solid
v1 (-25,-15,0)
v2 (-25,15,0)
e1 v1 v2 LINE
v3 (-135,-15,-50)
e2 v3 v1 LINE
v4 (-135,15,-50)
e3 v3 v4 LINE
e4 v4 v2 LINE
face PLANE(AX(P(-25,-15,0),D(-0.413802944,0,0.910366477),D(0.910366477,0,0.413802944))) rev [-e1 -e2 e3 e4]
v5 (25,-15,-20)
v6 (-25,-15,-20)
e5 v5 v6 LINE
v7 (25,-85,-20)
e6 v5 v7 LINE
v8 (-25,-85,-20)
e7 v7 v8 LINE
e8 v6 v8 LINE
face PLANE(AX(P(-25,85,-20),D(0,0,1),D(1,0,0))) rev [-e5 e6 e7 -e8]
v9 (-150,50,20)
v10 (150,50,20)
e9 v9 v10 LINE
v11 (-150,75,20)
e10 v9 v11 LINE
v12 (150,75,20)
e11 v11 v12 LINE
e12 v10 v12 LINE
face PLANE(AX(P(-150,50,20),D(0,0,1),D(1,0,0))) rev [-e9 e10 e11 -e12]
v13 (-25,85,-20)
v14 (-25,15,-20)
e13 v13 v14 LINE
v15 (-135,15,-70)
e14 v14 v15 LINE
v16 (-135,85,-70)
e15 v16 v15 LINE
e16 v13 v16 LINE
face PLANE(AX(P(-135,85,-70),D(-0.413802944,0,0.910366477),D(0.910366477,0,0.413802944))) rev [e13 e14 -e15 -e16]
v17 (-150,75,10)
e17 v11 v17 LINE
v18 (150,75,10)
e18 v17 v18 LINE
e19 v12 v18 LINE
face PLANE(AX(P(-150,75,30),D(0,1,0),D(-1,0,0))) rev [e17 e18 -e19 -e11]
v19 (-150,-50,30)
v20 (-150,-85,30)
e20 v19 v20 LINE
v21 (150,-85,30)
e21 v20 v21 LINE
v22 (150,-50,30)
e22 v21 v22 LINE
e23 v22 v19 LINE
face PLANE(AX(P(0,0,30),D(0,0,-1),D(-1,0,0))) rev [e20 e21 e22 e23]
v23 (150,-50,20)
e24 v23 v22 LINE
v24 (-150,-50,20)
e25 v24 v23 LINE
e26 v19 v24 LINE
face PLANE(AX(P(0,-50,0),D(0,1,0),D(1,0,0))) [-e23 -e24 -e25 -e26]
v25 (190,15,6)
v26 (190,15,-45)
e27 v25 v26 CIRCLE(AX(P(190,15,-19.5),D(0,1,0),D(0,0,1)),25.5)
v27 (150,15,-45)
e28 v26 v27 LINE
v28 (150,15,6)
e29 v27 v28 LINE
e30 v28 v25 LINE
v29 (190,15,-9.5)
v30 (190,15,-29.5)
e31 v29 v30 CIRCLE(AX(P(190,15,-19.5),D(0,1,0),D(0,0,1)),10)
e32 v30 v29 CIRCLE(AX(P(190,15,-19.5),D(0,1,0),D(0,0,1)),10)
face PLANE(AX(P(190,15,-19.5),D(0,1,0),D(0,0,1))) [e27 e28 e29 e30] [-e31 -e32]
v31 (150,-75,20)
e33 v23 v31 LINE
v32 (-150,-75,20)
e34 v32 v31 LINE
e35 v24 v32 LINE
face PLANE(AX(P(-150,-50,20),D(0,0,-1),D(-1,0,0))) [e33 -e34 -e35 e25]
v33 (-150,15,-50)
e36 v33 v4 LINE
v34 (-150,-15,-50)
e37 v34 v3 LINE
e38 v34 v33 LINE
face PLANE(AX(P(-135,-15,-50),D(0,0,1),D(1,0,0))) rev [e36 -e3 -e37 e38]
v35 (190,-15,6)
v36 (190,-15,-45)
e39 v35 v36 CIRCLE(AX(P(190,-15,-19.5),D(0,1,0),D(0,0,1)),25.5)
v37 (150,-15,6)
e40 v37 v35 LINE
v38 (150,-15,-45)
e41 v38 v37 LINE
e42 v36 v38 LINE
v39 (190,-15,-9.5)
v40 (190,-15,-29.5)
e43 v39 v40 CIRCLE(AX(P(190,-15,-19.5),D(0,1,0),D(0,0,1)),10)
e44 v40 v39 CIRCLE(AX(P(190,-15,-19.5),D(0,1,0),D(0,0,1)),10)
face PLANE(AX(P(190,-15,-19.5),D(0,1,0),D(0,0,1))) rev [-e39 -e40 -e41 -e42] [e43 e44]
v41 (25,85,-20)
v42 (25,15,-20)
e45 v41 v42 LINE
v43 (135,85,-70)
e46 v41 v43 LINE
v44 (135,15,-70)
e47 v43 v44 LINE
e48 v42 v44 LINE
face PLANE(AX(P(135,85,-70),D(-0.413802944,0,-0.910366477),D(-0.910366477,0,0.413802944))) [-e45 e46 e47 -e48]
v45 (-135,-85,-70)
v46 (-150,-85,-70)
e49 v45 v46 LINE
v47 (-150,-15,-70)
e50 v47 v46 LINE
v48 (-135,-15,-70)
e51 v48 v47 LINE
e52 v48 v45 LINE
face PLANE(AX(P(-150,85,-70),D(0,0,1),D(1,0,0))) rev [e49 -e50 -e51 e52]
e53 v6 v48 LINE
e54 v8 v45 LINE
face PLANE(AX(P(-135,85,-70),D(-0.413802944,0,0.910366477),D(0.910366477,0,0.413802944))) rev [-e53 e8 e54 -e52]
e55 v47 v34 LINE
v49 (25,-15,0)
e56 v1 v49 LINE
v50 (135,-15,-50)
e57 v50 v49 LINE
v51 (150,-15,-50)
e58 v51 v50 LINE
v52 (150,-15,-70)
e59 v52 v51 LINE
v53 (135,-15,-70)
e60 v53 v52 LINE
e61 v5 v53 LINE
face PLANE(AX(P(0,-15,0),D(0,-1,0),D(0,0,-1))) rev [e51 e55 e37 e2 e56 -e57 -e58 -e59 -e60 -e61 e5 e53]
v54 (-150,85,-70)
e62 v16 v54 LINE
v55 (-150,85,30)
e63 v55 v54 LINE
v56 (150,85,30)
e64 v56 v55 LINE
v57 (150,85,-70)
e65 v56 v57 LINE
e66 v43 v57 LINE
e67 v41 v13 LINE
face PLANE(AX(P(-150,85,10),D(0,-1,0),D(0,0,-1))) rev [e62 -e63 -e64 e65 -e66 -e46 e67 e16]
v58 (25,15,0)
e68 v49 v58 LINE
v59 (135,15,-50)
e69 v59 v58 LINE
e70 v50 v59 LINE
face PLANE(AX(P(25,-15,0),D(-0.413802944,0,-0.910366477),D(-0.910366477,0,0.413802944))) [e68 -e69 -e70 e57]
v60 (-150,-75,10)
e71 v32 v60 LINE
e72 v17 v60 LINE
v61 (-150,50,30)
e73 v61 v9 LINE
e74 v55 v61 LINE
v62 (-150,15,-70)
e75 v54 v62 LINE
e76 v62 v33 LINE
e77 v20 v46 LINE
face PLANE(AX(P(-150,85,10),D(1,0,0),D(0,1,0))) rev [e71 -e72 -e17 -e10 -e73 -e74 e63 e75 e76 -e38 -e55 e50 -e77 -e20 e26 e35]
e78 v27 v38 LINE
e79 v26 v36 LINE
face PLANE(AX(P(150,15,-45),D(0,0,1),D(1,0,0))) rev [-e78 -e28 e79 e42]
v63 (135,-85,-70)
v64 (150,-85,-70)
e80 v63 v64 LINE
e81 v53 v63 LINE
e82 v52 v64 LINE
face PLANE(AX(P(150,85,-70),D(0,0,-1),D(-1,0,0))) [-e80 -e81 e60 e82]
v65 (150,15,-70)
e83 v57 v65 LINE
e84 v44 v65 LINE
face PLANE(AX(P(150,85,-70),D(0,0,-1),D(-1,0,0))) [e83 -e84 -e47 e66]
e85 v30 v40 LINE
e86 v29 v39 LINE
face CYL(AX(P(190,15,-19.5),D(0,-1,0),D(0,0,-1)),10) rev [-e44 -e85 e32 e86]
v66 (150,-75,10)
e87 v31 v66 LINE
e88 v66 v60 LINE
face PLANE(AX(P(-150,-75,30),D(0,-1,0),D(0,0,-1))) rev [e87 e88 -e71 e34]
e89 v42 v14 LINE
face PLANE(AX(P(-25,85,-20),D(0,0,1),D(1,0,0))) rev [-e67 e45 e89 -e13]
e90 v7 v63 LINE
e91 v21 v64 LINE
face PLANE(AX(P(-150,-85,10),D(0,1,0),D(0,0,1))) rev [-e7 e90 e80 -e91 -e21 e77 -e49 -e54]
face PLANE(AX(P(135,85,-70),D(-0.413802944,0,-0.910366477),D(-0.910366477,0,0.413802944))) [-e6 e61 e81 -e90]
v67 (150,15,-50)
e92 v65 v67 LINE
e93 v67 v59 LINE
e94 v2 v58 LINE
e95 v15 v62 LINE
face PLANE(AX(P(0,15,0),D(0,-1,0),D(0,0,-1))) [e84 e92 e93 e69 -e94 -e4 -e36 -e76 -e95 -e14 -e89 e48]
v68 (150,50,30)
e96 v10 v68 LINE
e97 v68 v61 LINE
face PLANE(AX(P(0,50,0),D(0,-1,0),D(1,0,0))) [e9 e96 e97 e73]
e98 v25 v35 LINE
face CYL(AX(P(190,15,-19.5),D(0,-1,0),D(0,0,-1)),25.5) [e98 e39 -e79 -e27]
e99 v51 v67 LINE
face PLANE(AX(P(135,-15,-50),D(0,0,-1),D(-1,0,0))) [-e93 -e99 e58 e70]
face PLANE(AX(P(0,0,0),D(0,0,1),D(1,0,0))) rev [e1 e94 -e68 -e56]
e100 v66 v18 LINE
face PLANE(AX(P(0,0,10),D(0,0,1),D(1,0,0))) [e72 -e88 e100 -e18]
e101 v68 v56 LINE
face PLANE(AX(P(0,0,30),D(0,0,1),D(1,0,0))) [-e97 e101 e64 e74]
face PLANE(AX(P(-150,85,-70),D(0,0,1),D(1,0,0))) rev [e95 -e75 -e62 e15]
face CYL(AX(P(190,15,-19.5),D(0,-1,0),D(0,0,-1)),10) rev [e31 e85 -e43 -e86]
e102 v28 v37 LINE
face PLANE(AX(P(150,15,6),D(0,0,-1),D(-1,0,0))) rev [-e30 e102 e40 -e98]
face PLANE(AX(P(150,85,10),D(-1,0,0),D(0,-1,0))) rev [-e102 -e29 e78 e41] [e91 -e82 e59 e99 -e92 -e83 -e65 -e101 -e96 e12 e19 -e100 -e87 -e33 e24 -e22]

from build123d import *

# Parameters (mm, degrees)
SKETCH1_W           = 300
SKETCH1_H           = 170
BOSS_EXTRUDE1_DEPTH = 10
SKETCH2_W           = 300
SKETCH2_H           = 10
BOSS_EXTRUDE2_DEPTH = 20
SKETCH4_W           = 300
SKETCH4_H           = 10
BOSS_EXTRUDE3_DEPTH = 25
BOSS_EXTRUDE4_DEPTH = 85
CUT_EXTRUDE1_DEPTH  = 15
SKETCH8_R           = 10
BOSS_EXTRUDE5_DEPTH = 15


with BuildPart() as part:
    # Sketch1 → Boss-Extrude1 (new body)
    with BuildSketch(Plane.XY):
        Rectangle(SKETCH1_W, SKETCH1_H)
    extrude(amount=BOSS_EXTRUDE1_DEPTH)

    # Sketch2 → Boss-Extrude2 (add)
    with BuildSketch(Plane.XY.offset(10)):
        with Locations((0, 80)):
            Rectangle(SKETCH2_W, SKETCH2_H)
        with Locations((0, -80)):
            Rectangle(SKETCH2_W, SKETCH2_H)
    extrude(amount=BOSS_EXTRUDE2_DEPTH)

    # Sketch4 → Boss-Extrude3 (add)
    with BuildSketch(Plane.XZ.offset(-75)):
        with Locations((0, 25)):
            Rectangle(SKETCH4_W, SKETCH4_H)
    boss_extrude3 = extrude(amount=BOSS_EXTRUDE3_DEPTH)

    # Mirror1: Boss-Extrude3 across plane
    add(boss_extrude3.mirror(Plane.ZX))

    # Sketch5 → Boss-Extrude4 (add, symmetric)
    with BuildSketch(Plane(origin=(0, 0, 0), x_dir=(1, 0, 0), z_dir=(0, 1, 0))):
        Polygon((-150, 0), (-150, 70), (-135, 70), (-25, 20), (0, 20), (0, 0), align=None)
    boss_extrude4 = extrude(amount=BOSS_EXTRUDE4_DEPTH, both=True)

    # Sketch6 → Cut-Extrude1 (cut, symmetric)
    with BuildSketch(Plane(origin=(0, 0, 0), x_dir=(1, 0, 0), z_dir=(0, 1, 0))):
        Polygon((-150, 70), (-135, 70), (-25, 20), (0, 20), (0, 0), (-25, 0), (-135, 50), (-150, 50), align=None)
    cut_extrude1 = extrude(amount=CUT_EXTRUDE1_DEPTH, both=True, mode=Mode.SUBTRACT)

    # Mirror2: Boss-Extrude4, Cut-Extrude1 across plane
    add(boss_extrude4.mirror(Plane(origin=(0, 0, 0), x_dir=(0, 0, 1), z_dir=(1, 0, 0))))
    add(cut_extrude1.mirror(Plane(origin=(0, 0, 0), x_dir=(0, 0, 1), z_dir=(1, 0, 0))), mode=Mode.SUBTRACT)

    # Sketch8 → Boss-Extrude5 (add, symmetric)
    with BuildSketch(Plane(origin=(0, 0, 0), x_dir=(1, 0, 0), z_dir=(0, 1, 0))):
        with BuildLine():
            Line((150, -6), (190, -6))
            ThreePointArc((190, -6), (215.5, 19.5), (190, 45))
            Line((190, 45), (150, 45))
            Line((150, 45), (150, -6))
        make_face()
        with Locations(Location((190, 19.5, 0), (0, 0, 270))):
            Circle(SKETCH8_R, mode=Mode.SUBTRACT)
    extrude(amount=BOSS_EXTRUDE5_DEPTH, both=True)


solid = part.part
